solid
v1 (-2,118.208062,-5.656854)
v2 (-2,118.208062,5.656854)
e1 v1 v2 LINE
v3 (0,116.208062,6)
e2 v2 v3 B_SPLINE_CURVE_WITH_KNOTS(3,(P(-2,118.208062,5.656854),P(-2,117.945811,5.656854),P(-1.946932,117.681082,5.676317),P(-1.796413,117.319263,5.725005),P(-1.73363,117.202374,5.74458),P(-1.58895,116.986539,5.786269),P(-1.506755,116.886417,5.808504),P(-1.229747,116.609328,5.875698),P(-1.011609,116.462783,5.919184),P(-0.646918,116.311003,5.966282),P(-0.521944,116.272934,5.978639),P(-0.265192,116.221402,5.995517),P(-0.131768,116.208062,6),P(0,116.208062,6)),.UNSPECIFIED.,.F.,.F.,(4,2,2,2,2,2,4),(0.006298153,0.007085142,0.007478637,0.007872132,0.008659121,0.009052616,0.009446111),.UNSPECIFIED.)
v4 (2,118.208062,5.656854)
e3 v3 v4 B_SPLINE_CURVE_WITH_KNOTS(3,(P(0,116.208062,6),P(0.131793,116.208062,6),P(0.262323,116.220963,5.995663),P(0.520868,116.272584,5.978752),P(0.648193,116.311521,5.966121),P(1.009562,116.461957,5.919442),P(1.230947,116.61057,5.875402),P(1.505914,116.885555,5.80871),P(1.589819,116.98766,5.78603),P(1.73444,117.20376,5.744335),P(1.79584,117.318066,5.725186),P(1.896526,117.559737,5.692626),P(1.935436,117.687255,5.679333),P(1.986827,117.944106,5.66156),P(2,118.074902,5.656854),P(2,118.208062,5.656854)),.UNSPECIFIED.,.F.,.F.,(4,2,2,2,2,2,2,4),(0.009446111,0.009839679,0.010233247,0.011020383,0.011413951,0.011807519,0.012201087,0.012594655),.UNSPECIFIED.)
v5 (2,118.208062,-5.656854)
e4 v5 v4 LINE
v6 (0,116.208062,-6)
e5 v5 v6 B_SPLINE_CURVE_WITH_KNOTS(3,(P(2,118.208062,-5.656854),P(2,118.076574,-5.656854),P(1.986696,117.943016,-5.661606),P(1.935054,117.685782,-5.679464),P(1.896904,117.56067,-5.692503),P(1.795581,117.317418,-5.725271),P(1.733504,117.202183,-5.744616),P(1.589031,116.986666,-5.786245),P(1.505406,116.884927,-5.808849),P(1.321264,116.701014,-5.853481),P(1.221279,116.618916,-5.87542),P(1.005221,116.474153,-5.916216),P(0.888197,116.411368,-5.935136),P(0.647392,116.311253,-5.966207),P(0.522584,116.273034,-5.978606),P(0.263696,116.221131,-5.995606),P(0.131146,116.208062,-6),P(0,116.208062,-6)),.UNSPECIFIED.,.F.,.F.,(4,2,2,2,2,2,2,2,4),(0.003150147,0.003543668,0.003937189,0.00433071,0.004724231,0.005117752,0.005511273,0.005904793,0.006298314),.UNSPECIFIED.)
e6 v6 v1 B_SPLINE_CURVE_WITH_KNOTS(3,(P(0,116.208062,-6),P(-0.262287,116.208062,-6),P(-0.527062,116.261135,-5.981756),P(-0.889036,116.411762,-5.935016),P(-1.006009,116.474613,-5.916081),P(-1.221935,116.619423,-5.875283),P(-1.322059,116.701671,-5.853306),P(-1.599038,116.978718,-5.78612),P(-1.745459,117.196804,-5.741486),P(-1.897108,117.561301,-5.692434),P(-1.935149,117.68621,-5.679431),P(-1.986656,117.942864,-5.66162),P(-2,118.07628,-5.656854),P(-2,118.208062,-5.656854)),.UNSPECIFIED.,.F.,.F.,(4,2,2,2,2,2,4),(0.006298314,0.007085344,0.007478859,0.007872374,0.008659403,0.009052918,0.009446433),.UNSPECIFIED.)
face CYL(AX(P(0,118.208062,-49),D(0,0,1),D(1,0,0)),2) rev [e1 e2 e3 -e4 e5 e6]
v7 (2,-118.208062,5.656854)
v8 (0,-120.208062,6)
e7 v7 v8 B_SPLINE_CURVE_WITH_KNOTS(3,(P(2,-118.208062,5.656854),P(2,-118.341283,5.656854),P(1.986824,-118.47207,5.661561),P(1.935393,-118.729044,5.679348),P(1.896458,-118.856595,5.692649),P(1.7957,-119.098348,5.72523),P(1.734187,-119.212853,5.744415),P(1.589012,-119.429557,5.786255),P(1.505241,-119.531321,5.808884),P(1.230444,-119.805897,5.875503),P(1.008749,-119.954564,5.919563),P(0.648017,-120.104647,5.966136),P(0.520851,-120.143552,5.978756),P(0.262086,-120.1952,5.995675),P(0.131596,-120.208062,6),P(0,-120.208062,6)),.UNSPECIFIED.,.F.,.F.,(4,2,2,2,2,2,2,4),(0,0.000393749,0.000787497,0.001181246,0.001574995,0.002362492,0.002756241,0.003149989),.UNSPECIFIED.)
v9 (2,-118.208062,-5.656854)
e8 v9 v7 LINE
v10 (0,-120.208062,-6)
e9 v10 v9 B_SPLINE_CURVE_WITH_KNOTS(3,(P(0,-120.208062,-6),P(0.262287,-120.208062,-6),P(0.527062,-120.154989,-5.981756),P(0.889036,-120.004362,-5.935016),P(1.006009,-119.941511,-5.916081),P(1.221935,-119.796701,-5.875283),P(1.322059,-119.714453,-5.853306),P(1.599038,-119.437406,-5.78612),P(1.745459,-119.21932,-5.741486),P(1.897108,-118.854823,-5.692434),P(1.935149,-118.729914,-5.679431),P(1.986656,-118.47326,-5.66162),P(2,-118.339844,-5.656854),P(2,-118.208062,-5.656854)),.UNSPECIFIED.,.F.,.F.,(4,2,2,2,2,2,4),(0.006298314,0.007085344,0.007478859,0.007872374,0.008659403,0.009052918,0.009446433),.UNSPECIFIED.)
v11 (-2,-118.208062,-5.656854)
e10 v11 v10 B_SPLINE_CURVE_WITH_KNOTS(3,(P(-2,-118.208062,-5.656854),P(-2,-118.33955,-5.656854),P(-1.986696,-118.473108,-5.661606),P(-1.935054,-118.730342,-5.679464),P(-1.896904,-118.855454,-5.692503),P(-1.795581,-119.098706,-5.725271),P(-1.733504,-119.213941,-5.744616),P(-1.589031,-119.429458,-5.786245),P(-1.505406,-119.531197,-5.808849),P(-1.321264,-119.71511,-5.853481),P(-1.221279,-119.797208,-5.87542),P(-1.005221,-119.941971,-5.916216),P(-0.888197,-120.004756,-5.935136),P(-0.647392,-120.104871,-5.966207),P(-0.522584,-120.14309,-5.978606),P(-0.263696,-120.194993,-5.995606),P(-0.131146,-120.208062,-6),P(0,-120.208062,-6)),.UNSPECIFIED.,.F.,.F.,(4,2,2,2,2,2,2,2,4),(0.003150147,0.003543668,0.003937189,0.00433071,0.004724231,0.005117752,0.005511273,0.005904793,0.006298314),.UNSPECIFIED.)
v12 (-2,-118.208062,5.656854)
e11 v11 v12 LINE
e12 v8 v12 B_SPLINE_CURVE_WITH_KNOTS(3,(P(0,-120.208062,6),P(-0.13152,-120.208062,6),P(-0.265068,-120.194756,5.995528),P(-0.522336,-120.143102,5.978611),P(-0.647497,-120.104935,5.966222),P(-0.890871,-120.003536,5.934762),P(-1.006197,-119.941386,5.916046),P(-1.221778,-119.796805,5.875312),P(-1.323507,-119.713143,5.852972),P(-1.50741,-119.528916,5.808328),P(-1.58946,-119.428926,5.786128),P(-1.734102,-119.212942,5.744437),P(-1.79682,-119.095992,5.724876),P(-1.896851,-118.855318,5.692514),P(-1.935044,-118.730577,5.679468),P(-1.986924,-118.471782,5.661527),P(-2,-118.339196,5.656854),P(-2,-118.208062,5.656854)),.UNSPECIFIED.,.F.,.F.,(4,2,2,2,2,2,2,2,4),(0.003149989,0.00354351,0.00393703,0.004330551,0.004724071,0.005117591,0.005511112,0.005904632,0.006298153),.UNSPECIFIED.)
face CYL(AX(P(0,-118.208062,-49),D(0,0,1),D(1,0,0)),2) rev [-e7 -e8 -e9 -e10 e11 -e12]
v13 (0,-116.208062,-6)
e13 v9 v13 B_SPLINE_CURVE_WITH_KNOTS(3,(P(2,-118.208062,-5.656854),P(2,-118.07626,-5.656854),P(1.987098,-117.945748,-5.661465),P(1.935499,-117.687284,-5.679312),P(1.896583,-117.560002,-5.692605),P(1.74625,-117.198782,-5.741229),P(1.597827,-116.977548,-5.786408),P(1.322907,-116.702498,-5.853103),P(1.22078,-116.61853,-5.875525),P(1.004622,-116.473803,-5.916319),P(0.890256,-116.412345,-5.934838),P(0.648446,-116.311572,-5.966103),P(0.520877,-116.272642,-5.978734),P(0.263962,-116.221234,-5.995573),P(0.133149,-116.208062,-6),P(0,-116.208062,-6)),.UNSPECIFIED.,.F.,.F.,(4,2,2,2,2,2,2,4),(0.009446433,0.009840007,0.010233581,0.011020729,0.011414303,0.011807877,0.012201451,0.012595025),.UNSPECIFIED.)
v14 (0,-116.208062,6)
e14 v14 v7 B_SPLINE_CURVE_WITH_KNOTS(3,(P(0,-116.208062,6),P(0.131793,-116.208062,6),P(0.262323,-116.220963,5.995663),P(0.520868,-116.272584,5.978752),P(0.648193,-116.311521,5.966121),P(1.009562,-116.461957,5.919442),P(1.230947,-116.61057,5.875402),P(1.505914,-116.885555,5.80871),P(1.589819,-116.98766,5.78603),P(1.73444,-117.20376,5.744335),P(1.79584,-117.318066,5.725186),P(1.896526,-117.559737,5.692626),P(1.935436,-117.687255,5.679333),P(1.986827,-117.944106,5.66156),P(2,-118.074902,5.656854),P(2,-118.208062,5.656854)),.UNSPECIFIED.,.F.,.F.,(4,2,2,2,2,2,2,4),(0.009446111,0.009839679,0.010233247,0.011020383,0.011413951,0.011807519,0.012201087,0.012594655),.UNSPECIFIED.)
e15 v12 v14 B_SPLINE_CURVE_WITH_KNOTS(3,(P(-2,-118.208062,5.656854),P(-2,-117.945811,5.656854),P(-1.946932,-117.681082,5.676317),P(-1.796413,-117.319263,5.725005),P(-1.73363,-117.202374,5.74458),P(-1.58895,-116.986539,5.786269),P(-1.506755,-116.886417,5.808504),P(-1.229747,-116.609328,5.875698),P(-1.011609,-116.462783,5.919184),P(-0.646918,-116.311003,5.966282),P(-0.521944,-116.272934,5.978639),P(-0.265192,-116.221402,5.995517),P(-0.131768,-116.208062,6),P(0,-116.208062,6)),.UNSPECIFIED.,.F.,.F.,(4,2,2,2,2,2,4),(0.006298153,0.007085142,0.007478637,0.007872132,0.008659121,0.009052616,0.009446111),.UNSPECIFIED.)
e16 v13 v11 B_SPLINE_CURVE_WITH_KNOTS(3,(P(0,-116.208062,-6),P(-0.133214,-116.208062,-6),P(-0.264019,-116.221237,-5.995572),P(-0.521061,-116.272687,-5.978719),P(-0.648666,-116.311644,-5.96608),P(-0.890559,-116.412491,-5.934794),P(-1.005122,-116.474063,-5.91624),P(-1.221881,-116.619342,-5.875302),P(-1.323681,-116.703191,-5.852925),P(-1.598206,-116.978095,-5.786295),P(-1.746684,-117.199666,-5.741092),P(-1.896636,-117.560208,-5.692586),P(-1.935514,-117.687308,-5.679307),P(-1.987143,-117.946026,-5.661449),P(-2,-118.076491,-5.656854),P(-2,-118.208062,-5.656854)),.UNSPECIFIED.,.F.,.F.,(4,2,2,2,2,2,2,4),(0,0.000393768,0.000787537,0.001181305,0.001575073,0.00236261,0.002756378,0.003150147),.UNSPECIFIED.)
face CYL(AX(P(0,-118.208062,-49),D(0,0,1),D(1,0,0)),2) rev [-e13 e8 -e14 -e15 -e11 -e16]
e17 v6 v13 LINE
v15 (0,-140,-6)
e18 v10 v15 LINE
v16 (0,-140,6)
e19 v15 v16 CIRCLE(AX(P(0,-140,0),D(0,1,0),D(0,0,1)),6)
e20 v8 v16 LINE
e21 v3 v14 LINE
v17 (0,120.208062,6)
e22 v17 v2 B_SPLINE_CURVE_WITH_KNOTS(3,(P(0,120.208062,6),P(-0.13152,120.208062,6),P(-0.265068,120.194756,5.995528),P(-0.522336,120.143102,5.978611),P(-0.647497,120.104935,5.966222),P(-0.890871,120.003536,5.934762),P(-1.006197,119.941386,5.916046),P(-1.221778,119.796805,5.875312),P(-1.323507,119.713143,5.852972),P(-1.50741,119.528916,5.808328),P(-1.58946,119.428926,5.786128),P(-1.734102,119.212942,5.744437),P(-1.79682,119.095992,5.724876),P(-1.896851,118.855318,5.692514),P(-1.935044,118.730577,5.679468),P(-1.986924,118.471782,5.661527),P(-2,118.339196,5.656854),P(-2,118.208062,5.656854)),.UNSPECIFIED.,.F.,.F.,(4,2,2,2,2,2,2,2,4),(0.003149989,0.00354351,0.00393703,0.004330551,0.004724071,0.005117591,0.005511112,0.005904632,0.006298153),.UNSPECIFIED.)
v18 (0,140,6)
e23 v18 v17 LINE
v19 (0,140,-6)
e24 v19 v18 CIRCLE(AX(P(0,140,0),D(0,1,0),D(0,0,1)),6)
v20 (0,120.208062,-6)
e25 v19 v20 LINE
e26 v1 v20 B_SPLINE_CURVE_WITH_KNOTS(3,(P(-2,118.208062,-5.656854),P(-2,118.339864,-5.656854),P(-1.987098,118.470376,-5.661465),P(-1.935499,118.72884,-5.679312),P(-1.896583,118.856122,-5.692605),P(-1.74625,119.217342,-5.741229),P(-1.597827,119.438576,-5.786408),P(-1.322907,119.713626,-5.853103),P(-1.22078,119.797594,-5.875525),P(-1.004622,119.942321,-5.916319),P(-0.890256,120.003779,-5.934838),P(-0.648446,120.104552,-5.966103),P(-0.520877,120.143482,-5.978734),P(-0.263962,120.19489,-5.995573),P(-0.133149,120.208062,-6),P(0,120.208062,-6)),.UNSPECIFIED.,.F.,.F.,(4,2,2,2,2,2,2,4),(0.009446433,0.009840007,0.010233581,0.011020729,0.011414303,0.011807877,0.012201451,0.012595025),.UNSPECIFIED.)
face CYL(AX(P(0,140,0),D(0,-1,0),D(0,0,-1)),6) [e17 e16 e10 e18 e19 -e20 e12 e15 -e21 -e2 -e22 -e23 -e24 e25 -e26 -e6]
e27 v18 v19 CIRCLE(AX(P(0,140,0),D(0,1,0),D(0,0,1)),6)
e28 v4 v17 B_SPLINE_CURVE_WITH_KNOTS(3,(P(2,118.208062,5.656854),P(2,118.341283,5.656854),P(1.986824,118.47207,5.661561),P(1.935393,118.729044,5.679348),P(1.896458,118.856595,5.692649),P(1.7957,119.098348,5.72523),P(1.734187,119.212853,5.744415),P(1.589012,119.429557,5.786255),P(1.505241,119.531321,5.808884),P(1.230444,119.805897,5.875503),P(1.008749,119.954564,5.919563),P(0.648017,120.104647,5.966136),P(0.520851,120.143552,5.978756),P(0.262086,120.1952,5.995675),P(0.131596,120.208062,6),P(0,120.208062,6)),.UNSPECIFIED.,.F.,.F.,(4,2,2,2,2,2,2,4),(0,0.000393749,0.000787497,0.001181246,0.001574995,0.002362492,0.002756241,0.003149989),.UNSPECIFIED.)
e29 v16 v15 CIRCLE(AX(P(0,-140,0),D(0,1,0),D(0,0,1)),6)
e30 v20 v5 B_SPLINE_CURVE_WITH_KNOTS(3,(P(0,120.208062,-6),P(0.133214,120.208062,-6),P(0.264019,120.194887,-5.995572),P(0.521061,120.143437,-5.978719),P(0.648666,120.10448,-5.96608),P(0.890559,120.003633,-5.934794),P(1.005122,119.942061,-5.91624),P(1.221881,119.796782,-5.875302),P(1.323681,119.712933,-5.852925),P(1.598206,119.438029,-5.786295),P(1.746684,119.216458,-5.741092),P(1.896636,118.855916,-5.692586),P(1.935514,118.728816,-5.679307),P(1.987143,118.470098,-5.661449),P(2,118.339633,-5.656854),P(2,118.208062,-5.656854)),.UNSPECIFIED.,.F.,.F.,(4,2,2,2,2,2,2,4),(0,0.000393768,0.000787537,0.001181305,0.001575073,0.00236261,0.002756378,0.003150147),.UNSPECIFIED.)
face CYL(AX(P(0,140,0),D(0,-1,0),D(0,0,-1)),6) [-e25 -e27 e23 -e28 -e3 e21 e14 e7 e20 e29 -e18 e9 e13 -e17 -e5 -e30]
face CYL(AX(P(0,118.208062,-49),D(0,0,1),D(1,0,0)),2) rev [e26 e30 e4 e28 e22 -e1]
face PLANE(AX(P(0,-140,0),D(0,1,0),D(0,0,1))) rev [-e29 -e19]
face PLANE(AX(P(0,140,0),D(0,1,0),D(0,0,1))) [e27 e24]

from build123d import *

# Parameters (mm, degrees)
SKETCH_1_R          = 6
EXTRUDE_1_DEPTH     = 140
SKETCH_3_R          = 2
CUT_EXTRUDE_1_DEPTH = 60


with BuildPart() as part:
    # 草图1 → 凸台-拉伸1 (new, symmetric)
    with BuildSketch(Plane(origin=(0, 0, 0), x_dir=(1, 0, 0), z_dir=(0, 1, 0))):
        with Locations(Location((0, 0, 0), (0, 0, 270))):
            Circle(SKETCH_1_R)
    extrude(amount=EXTRUDE_1_DEPTH, both=True)

    # 草图3 → 切除-拉伸1 (cut)
    with BuildSketch(Plane.XY.offset(11)):
        with Locations(Location((0, -118.208062, 0), (0, 0, 89.999999987))):
            Circle(SKETCH_3_R)
    cut_extrude_1 = extrude(amount=-CUT_EXTRUDE_1_DEPTH, mode=Mode.SUBTRACT)

    # 镜向1: 切除-拉伸1 across plane
    add(cut_extrude_1.mirror(Plane.ZX), mode=Mode.SUBTRACT)


solid = part.part
